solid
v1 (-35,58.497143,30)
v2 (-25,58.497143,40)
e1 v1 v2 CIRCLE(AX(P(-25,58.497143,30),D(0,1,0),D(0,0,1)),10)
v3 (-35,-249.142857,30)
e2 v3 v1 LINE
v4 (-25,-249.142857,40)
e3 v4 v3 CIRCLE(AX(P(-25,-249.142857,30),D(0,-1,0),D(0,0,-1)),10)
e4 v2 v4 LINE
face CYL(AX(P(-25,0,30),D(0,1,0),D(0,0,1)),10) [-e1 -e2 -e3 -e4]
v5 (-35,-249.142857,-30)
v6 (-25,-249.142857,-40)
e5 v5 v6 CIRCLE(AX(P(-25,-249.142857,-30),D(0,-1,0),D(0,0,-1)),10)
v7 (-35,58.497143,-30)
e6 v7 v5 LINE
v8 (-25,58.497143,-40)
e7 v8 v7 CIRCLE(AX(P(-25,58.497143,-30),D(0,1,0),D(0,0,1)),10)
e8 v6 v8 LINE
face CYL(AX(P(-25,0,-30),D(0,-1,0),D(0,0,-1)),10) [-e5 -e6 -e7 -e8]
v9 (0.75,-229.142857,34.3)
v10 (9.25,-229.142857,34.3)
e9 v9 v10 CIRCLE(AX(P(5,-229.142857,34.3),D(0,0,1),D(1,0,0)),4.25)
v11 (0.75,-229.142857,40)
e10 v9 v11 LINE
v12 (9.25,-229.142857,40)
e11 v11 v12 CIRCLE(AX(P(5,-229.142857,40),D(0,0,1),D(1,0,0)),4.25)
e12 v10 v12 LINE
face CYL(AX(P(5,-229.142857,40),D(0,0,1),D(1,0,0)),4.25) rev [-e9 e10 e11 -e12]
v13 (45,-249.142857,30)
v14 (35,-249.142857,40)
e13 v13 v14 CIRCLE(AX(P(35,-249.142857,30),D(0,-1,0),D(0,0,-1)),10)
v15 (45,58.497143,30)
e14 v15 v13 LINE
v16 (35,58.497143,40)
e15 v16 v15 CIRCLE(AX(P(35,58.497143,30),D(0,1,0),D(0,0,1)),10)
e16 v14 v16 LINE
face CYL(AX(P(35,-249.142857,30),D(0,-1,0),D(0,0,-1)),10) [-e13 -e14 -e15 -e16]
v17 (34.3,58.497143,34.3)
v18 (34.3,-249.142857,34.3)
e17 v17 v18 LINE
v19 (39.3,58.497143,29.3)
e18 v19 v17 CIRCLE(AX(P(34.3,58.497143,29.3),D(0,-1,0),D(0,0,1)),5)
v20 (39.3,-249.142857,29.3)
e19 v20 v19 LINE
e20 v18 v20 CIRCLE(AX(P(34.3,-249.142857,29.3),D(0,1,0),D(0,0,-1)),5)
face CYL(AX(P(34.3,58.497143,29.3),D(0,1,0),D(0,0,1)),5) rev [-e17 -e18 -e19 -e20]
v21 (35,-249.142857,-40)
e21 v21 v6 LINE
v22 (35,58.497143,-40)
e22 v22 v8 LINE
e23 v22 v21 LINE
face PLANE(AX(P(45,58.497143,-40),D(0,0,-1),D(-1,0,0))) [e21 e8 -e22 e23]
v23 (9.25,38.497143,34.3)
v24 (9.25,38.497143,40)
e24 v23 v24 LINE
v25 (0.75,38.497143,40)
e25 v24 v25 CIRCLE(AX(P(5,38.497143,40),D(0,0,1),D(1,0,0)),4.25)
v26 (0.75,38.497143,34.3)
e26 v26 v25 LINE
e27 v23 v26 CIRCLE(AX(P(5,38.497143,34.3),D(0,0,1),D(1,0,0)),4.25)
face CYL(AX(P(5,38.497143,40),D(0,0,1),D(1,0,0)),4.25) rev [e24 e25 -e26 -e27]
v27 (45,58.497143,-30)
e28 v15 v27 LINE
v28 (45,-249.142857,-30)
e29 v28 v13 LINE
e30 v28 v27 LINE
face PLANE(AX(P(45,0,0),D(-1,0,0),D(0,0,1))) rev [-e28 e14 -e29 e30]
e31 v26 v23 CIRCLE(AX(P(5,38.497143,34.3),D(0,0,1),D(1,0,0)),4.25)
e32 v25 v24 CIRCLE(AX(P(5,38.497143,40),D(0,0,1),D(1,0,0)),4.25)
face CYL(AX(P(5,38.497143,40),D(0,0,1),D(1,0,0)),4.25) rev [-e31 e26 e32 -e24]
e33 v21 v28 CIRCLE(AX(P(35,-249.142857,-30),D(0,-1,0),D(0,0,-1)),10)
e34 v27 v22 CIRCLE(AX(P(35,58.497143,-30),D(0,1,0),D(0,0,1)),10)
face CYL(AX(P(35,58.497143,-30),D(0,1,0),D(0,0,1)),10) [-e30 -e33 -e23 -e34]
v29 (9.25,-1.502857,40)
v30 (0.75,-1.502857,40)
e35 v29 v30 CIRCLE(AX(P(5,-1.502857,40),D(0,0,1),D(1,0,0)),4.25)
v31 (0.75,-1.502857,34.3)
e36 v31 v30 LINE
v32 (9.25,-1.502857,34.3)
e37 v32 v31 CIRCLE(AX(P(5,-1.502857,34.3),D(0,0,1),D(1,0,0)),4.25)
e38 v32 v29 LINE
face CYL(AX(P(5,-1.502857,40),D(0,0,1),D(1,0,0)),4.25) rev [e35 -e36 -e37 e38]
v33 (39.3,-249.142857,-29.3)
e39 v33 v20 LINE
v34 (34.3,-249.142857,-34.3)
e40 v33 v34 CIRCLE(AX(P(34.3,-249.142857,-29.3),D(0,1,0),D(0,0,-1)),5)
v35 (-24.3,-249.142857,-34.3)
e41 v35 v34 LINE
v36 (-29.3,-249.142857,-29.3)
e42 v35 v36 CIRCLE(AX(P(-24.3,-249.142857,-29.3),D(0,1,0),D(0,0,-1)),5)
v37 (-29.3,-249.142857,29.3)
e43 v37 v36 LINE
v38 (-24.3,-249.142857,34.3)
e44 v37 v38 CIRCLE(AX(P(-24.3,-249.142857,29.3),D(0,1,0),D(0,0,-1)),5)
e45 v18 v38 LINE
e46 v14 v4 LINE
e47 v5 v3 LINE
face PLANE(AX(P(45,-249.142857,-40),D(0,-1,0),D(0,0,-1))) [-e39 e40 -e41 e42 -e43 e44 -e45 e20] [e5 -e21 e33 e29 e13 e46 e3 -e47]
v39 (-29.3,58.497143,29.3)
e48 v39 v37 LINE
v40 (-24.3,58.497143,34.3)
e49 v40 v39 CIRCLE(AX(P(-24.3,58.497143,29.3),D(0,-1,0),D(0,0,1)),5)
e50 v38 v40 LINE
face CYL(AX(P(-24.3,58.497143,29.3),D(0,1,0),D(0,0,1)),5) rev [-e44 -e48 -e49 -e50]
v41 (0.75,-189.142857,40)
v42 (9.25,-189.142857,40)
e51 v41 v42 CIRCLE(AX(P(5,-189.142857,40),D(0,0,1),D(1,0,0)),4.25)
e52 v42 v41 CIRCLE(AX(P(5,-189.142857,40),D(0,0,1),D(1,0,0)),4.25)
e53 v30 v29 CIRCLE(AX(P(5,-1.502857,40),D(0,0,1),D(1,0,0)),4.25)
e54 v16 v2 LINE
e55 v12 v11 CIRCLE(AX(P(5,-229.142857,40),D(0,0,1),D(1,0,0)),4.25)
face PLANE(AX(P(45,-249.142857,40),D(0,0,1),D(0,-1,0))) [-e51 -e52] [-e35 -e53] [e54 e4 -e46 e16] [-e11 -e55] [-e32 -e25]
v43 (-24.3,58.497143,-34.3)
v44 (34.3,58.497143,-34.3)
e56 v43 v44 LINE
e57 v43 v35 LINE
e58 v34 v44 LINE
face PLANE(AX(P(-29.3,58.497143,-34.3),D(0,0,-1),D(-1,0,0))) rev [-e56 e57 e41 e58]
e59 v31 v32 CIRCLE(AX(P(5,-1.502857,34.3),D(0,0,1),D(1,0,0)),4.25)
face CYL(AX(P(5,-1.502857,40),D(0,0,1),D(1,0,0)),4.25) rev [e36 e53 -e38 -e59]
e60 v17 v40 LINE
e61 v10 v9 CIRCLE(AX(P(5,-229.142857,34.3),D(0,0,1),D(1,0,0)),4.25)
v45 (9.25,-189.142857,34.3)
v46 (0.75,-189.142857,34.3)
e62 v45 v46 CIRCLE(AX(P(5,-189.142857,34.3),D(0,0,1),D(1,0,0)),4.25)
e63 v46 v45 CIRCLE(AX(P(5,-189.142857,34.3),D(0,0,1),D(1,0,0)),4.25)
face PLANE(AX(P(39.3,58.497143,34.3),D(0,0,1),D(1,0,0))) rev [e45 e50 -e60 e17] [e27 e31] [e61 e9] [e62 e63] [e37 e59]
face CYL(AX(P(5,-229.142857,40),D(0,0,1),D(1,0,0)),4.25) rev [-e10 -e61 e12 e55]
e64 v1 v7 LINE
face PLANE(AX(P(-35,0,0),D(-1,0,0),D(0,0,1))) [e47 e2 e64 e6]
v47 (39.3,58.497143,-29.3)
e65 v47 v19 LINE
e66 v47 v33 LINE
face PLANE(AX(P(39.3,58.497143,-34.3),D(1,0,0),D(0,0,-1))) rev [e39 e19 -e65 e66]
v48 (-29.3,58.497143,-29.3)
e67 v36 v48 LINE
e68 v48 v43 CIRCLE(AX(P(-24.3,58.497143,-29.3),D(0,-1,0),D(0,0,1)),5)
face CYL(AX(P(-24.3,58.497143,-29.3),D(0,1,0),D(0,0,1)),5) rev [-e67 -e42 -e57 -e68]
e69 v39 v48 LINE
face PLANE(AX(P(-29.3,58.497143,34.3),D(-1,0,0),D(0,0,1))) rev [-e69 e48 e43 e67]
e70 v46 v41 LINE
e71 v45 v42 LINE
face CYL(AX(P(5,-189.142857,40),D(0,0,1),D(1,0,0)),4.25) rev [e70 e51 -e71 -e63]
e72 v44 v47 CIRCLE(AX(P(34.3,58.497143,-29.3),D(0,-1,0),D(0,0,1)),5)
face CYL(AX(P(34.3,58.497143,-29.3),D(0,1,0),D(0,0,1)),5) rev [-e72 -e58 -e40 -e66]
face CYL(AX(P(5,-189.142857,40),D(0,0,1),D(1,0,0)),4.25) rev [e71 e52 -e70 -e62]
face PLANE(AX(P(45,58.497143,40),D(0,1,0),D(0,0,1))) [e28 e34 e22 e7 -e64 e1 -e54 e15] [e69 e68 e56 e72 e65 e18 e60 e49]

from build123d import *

# Parameters (mm, degrees)
SKETCH1_W                      = 307.64
SKETCH1_H                      = 80
BOSS_EXTRUDE1_DEPTH            = 80
SKETCH2_W                      = 68.6
SKETCH2_H                      = 68.6
CUT_EXTRUDE1_DEPTH             = 314.476266406
F_8_5_8_5_DIAMETER_HOLE2_D     = 8.5
F_8_5_8_5_DIAMETER_HOLE2_DEPTH = 5.7
FILLET1_R                      = 5
FILLET2_R                      = 10
F_8_5_8_5_DIAMETER_HOLE3_D     = 8.5
F_8_5_8_5_DIAMETER_HOLE3_DEPTH = 10
F_8_5_8_5_DIAMETER_HOLE3_TIP   = 2.553657631
F_8_5_8_5_DIAMETER_HOLE5_D     = 8.5
F_8_5_8_5_DIAMETER_HOLE5_DEPTH = 10
F_8_5_8_5_DIAMETER_HOLE5_TIP   = 2.553657631


with BuildPart() as part:
    # Sketch1 → Boss-Extrude1 (new body)
    with BuildSketch(Plane(origin=(-35, 0, 0), x_dir=(0, -1, 0), z_dir=(-1, 0, 0))):
        with Locations((95.322857143, 0)):
            Rectangle(SKETCH1_W, SKETCH1_H)
    extrude(amount=-BOSS_EXTRUDE1_DEPTH)

    # Sketch2 → Cut-Extrude1 (cut, through all)
    with BuildSketch(Plane.XZ.offset(249.142857143)):
        with Locations((5, 0)):
            Rectangle(SKETCH2_W, SKETCH2_H)
    extrude(amount=-CUT_EXTRUDE1_DEPTH, mode=Mode.SUBTRACT)

    # Ø8.5 (8.5) Diameter Hole2
    with Locations(Plane.XY.offset(40)):
        with Locations((5, -189.142857143), (5, -229.142857143)):
            Hole(F_8_5_8_5_DIAMETER_HOLE2_D / 2, depth=F_8_5_8_5_DIAMETER_HOLE2_DEPTH)

    # Fillet1
    fillet1_edges = [part.edges().sort_by_distance(p)[0] for p in [
        (-29.3, -95.322857143, -34.3),
        (-29.3, -95.322857143, 34.3),
        (39.3, -95.322857143, 34.3),
        (39.3, -95.322857143, -34.3),
    ]]
    fillet(fillet1_edges, radius=FILLET1_R)

    # Fillet2
    fillet2_edges = [part.edges().sort_by_distance(p)[0] for p in [
        (45, -95.322857143, 40),
        (45, -95.322857143, -40),
        (-35, -95.322857143, 40),
        (-35, -95.322857143, -40),
    ]]
    fillet(fillet2_edges, radius=FILLET2_R)

    # Ø8.5 (8.5) Diameter Hole3
    with Locations(Plane.XY.offset(40)):
        with Locations((5, 38.497142857)):
            Hole(F_8_5_8_5_DIAMETER_HOLE3_D / 2, depth=F_8_5_8_5_DIAMETER_HOLE3_DEPTH)
            with Locations((0, 0, -(F_8_5_8_5_DIAMETER_HOLE3_DEPTH + F_8_5_8_5_DIAMETER_HOLE3_TIP / 2))):  # 118° drill point
                Cone(0, F_8_5_8_5_DIAMETER_HOLE3_D / 2, F_8_5_8_5_DIAMETER_HOLE3_TIP, mode=Mode.SUBTRACT)

    # Ø8.5 (8.5) Diameter Hole5
    with Locations(Plane.XY.offset(40)):
        with Locations((5, -1.502857143)):
            Hole(F_8_5_8_5_DIAMETER_HOLE5_D / 2, depth=F_8_5_8_5_DIAMETER_HOLE5_DEPTH)
            with Locations((0, 0, -(F_8_5_8_5_DIAMETER_HOLE5_DEPTH + F_8_5_8_5_DIAMETER_HOLE5_TIP / 2))):  # 118° drill point
                Cone(0, F_8_5_8_5_DIAMETER_HOLE5_D / 2, F_8_5_8_5_DIAMETER_HOLE5_TIP, mode=Mode.SUBTRACT)


solid = part.part
